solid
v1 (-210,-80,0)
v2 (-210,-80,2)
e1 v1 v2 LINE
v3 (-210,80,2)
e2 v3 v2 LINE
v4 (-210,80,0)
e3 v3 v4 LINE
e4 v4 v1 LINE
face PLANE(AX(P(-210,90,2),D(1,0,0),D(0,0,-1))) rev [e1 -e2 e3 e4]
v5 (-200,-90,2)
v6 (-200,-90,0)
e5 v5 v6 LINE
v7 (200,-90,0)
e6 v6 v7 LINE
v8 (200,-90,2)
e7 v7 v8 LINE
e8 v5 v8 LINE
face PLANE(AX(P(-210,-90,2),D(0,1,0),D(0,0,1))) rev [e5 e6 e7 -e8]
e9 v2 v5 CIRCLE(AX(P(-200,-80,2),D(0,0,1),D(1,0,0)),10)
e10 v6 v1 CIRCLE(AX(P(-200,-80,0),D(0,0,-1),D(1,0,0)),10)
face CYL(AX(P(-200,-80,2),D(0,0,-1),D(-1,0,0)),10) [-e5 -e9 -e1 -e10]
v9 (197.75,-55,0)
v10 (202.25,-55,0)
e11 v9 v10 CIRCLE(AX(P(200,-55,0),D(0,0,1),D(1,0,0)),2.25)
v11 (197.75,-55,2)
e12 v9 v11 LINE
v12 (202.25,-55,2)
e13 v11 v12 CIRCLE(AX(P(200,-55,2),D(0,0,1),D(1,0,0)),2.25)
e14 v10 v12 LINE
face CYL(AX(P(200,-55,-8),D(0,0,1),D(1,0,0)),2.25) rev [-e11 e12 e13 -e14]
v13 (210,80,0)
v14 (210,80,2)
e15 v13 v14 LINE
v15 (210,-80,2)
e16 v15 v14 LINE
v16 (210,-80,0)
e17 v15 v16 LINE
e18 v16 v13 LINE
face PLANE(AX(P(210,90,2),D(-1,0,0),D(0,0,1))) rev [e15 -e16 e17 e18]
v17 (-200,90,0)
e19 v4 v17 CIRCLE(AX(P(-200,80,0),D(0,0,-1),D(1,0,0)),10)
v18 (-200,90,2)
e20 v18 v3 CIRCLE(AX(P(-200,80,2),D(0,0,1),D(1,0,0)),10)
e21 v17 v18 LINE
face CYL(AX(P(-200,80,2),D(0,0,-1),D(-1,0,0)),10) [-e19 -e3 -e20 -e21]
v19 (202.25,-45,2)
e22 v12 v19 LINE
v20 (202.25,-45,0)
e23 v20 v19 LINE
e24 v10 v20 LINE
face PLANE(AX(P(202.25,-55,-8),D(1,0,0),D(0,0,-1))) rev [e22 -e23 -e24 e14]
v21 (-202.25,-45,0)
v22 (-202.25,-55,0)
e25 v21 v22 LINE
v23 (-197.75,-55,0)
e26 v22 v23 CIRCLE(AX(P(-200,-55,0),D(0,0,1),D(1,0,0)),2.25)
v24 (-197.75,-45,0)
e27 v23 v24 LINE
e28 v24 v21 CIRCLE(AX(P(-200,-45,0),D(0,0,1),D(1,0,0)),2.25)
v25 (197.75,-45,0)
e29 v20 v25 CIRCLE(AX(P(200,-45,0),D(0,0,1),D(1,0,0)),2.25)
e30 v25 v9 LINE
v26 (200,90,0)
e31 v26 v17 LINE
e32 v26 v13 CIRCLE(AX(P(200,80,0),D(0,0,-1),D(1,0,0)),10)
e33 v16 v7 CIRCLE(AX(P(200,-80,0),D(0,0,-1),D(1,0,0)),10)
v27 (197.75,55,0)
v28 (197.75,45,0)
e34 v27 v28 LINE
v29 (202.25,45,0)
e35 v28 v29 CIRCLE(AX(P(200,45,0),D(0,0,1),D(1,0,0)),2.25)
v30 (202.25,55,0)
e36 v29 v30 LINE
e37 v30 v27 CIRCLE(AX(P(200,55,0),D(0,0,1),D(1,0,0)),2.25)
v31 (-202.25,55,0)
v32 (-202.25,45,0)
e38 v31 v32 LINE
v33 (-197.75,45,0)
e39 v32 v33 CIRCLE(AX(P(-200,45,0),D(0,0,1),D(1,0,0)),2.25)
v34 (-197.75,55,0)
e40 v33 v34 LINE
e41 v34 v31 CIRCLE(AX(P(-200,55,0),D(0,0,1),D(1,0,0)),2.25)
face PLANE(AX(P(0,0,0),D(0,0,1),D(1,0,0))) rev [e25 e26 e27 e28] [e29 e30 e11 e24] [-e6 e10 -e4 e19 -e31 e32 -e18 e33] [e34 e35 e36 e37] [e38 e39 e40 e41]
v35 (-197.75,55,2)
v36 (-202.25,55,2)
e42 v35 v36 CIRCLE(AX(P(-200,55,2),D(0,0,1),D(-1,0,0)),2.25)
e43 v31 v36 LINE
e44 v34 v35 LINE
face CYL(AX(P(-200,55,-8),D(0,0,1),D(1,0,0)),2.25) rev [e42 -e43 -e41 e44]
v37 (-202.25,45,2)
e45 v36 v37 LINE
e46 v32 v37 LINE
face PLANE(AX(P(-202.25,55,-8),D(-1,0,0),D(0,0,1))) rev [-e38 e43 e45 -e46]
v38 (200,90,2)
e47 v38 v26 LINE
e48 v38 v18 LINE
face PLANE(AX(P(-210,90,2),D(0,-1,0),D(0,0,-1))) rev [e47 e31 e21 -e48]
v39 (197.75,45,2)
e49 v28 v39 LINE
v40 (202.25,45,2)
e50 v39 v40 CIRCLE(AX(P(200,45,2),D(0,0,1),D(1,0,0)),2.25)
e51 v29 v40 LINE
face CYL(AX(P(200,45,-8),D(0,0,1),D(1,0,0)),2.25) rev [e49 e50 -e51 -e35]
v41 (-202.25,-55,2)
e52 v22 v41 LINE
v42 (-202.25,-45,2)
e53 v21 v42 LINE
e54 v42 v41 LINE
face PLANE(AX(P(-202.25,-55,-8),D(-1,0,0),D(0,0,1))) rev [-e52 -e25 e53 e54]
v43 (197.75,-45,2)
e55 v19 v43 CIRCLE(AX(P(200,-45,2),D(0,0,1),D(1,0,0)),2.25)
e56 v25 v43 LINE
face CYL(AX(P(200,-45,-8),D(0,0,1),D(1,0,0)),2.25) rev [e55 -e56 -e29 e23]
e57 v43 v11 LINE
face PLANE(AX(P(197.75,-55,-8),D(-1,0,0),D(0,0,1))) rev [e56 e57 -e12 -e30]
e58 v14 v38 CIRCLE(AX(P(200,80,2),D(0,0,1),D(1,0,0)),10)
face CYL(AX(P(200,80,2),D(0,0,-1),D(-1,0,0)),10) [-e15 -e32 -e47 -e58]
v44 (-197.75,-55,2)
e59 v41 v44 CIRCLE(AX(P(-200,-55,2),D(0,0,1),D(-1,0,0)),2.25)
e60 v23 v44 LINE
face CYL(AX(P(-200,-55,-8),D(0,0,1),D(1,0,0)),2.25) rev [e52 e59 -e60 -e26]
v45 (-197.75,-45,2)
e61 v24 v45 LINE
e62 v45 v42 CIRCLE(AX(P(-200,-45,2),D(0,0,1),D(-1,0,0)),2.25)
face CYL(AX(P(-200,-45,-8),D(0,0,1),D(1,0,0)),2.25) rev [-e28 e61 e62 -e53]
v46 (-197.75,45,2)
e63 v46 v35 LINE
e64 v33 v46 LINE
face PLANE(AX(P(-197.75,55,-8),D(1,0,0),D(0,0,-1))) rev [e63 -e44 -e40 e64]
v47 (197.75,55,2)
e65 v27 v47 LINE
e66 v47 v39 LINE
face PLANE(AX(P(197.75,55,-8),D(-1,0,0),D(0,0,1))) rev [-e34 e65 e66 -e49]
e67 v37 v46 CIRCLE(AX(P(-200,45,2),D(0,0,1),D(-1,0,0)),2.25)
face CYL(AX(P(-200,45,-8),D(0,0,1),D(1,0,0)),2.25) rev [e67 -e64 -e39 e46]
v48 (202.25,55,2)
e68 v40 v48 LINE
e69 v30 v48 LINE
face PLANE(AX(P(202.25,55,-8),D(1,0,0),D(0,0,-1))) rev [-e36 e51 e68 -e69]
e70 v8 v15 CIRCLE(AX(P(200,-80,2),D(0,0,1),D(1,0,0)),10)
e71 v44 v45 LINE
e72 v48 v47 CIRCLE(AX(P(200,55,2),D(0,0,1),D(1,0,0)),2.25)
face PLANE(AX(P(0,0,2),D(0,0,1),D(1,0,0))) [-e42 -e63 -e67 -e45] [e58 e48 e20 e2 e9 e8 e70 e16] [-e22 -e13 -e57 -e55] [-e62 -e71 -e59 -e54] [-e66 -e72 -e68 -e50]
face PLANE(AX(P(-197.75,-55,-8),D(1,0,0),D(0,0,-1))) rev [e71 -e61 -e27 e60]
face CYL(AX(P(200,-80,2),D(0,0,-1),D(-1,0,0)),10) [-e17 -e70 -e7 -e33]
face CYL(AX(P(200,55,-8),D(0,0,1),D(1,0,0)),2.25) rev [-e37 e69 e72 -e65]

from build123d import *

# Parameters (mm, degrees)
SKETCH_1_W          = 420
SKETCH_1_H          = 180
EXTRUDE_1_DEPTH     = 2
HOLE_WIZARD_M4_2_D  = 3.3
CUT_EXTRUDE_1_DEPTH = 10
FILLET_1_R          = 10


with BuildPart() as part:
    # 草图1 → 凸台-拉伸1 (new body)
    with BuildSketch(Plane.XY):
        Rectangle(SKETCH_1_W, SKETCH_1_H)
    extrude(amount=EXTRUDE_1_DEPTH)

    # M4 螺纹孔的螺纹孔钻头2 (through all)
    with Locations(Plane.XY.offset(2)):
        with Locations((200, 50), (-200, -50), (-200, 50), (200, -50)):
            Hole(HOLE_WIZARD_M4_2_D / 2)

    # 草图4 → 切除-拉伸1 (cut)
    with BuildSketch(Plane.XY.offset(2)):
        with BuildLine():
            Line((202.25, 55), (202.25, 45))
            ThreePointArc((202.25, 45), (200, 42.75), (197.75, 45))
            Line((197.75, 45), (197.75, 55))
            ThreePointArc((197.75, 55), (200, 57.25), (202.25, 55))
        make_face()
        with BuildLine():
            Line((197.75, -55), (197.75, -45))
            ThreePointArc((197.75, -45), (200, -42.75), (202.25, -45))
            Line((202.25, -45), (202.25, -55))
            ThreePointArc((202.25, -55), (200, -57.25), (197.75, -55))
        make_face()
        with BuildLine():
            Line((-197.75, -55), (-197.75, -45))
            ThreePointArc((-197.75, -45), (-200, -42.75), (-202.25, -45))
            Line((-202.25, -45), (-202.25, -55))
            ThreePointArc((-202.25, -55), (-200, -57.25), (-197.75, -55))
        make_face()
        with BuildLine():
            Line((-202.25, 55), (-202.25, 45))
            ThreePointArc((-202.25, 45), (-200, 42.75), (-197.75, 45))
            Line((-197.75, 45), (-197.75, 55))
            ThreePointArc((-197.75, 55), (-200, 57.25), (-202.25, 55))
        make_face()
    extrude(amount=-CUT_EXTRUDE_1_DEPTH, mode=Mode.SUBTRACT)

    # 圆角1
    fillet_1_edges = [part.edges().sort_by_distance(p)[0] for p in [
        (210, -90, 1),
        (-210, -90, 1),
        (-210, 90, 1),
        (210, 90, 1),
    ]]
    fillet(fillet_1_edges, radius=FILLET_1_R)


solid = part.part
